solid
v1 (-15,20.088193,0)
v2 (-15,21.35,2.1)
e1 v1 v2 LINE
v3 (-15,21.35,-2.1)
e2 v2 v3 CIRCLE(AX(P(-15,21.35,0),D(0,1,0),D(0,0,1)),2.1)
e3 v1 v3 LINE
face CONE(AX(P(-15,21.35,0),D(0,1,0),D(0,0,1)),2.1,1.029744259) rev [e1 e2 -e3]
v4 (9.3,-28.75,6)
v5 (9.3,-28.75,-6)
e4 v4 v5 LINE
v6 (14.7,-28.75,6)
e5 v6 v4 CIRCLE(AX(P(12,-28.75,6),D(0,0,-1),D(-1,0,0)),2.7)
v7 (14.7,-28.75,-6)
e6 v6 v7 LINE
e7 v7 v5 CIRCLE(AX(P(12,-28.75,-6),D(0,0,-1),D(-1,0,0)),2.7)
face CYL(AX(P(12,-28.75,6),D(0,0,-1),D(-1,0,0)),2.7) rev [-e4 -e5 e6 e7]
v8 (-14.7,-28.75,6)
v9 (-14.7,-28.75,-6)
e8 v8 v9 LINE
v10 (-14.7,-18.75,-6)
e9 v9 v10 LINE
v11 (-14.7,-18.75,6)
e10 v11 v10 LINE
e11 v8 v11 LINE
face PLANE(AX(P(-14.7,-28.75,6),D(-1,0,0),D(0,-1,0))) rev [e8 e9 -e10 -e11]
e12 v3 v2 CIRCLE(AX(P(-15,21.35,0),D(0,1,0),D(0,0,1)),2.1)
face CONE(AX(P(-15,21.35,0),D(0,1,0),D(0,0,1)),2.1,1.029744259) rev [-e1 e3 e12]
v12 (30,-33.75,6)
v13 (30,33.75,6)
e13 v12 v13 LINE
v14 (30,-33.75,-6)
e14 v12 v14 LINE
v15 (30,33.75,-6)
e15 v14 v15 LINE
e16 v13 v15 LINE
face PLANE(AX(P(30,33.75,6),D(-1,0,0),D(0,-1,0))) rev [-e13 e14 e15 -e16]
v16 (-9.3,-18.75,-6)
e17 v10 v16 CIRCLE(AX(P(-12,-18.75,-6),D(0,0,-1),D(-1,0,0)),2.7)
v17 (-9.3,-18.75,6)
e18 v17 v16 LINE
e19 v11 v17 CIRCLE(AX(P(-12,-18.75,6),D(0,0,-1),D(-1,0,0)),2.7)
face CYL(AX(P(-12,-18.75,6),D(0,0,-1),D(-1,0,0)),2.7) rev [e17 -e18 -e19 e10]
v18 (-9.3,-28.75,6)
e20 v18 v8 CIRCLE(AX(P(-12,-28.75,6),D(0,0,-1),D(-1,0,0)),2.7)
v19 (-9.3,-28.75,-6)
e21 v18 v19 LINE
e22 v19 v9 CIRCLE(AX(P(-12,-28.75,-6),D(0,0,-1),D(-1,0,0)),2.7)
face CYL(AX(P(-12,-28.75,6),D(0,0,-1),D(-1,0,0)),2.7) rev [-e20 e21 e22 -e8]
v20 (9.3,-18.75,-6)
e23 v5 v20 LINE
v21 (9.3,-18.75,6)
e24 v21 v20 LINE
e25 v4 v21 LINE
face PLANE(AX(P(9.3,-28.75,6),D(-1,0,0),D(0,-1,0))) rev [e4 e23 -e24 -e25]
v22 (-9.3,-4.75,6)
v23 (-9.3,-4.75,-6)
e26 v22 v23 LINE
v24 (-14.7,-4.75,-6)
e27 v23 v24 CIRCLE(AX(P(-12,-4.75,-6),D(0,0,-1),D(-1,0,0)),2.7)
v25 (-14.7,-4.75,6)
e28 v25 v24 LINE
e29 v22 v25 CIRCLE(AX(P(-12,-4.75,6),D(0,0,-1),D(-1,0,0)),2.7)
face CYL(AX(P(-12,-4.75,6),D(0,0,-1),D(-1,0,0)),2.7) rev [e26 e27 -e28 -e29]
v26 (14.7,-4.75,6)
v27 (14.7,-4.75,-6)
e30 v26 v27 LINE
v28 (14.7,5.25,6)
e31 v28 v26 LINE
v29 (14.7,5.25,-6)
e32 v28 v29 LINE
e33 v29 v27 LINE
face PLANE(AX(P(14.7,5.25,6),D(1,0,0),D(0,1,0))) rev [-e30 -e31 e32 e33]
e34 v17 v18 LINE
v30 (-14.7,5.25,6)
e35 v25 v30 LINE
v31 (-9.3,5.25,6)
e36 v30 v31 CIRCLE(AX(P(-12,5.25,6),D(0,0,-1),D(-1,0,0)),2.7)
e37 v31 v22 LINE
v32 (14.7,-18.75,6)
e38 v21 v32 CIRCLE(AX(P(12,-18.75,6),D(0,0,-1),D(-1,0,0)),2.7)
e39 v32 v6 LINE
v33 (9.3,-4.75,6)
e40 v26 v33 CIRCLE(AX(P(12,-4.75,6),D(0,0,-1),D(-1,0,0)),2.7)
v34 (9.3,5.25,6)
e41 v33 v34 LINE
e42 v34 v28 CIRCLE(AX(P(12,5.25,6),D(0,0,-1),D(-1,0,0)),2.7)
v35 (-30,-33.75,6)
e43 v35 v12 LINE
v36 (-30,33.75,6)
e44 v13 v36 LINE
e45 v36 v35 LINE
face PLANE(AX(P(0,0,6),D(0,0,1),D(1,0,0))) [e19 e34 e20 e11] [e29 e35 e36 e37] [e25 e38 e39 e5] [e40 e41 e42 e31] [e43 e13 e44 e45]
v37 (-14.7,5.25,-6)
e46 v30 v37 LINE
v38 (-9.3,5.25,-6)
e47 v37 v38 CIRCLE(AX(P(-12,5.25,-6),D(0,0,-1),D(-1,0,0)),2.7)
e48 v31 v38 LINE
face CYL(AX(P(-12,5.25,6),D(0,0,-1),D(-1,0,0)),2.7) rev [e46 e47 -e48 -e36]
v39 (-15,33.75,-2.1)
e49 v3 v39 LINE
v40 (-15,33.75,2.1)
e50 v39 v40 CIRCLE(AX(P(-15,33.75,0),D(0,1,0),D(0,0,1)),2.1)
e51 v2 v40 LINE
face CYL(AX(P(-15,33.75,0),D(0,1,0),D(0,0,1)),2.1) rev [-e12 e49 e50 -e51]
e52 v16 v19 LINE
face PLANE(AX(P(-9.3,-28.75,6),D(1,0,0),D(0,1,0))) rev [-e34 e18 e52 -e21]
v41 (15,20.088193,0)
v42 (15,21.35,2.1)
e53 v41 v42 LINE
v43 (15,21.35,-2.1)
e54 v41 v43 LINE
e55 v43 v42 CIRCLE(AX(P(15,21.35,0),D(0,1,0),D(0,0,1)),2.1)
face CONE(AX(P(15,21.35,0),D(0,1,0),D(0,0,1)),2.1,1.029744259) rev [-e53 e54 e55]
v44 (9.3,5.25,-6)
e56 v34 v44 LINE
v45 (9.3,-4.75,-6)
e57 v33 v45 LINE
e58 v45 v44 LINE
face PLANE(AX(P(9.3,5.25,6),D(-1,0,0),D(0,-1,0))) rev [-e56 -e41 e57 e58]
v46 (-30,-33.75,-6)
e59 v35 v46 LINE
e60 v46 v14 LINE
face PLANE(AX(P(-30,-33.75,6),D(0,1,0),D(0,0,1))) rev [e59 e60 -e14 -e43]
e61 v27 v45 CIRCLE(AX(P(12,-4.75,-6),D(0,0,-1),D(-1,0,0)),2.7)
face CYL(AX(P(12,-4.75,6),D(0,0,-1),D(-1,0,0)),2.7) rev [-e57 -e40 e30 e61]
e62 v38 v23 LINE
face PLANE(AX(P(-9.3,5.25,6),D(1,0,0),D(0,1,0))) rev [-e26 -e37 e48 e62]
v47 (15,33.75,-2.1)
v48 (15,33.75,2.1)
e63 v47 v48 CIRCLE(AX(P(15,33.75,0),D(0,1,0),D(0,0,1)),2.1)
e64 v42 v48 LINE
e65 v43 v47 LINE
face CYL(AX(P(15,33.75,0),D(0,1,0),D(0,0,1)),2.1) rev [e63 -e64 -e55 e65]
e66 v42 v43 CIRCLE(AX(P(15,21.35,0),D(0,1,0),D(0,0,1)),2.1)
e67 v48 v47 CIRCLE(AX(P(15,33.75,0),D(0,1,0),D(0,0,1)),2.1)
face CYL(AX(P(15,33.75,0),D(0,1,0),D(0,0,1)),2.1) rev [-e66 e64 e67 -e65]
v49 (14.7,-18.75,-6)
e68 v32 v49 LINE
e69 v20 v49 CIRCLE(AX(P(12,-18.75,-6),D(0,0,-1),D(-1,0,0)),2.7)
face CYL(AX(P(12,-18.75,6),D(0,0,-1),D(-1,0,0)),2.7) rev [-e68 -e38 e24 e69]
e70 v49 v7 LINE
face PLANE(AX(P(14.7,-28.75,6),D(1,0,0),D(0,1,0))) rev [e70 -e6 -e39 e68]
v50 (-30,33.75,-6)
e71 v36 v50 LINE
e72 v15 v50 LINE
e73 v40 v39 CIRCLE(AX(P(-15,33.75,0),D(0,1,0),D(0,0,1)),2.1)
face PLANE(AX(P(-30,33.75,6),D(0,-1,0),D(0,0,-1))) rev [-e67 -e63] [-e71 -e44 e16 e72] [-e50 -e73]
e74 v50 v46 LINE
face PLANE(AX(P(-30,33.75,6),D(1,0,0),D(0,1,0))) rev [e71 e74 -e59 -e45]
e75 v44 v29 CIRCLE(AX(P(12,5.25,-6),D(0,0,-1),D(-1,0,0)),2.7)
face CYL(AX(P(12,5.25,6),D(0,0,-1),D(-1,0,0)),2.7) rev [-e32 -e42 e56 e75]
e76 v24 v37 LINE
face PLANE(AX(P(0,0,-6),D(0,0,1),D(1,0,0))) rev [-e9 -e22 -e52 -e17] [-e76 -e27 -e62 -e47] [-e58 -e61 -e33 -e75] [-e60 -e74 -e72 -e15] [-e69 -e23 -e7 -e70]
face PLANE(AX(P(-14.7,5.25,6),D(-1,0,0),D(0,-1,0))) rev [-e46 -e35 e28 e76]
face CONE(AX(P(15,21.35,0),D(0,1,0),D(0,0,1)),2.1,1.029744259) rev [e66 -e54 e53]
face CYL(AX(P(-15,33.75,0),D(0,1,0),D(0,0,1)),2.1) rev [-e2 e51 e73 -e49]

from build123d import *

# Parameters (mm, degrees)
SKETCH_1_W             = 60
SKETCH_1_H             = 67.5
EXTRUDE_1_DEPTH        = 6
CUT_EXTRUDE_1_DEPTH    = 47.723254382
HOLE_WIZARD_M5_1_D     = 4.2
HOLE_WIZARD_M5_1_DEPTH = 12.4
HOLE_WIZARD_M5_1_TIP   = 1.2618073


with BuildPart() as part:
    # 草图1 → 凸台-拉伸1 (new, symmetric)
    with BuildSketch(Plane.XY):
        Rectangle(SKETCH_1_W, SKETCH_1_H)
    extrude(amount=EXTRUDE_1_DEPTH, both=True)

    # 草图2 → 切除-拉伸1 (cut, through all)
    with BuildSketch(Plane(origin=(0, 0, -6), x_dir=(-1, 0, 0), z_dir=(0, 0, -1))):
        with BuildLine():
            Line((9.3, -28.75), (9.3, -18.75))
            ThreePointArc((9.3, -18.75), (12, -16.05), (14.7, -18.75))
            Line((14.7, -18.75), (14.7, -28.75))
            ThreePointArc((14.7, -28.75), (12, -31.45), (9.3, -28.75))
        make_face()
        with BuildLine():
            Line((-14.7, -28.75), (-14.7, -18.75))
            ThreePointArc((-14.7, -18.75), (-12, -16.05), (-9.3, -18.75))
            Line((-9.3, -18.75), (-9.3, -28.75))
            ThreePointArc((-9.3, -28.75), (-12, -31.45), (-14.7, -28.75))
        make_face()
        with BuildLine():
            Line((14.7, 5.25), (14.7, -4.75))
            ThreePointArc((14.7, -4.75), (12, -7.45), (9.3, -4.75))
            Line((9.3, -4.75), (9.3, 5.25))
            ThreePointArc((9.3, 5.25), (12, 7.95), (14.7, 5.25))
        make_face()
        with BuildLine():
            Line((-9.3, 5.25), (-9.3, -4.75))
            ThreePointArc((-9.3, -4.75), (-12, -7.45), (-14.7, -4.75))
            Line((-14.7, -4.75), (-14.7, 5.25))
            ThreePointArc((-14.7, 5.25), (-12, 7.95), (-9.3, 5.25))
        make_face()
    extrude(amount=-CUT_EXTRUDE_1_DEPTH, mode=Mode.SUBTRACT)

    # M5 螺纹孔1
    with Locations(Plane(origin=(0, 33.75, 0), x_dir=(1, 0, 0), z_dir=(0, 1, 0))):
        with Locations((-15, 0), (15, 0)):
            Hole(HOLE_WIZARD_M5_1_D / 2, depth=HOLE_WIZARD_M5_1_DEPTH)
            with Locations((0, 0, -(HOLE_WIZARD_M5_1_DEPTH + HOLE_WIZARD_M5_1_TIP / 2))):  # 118° drill point
                Cone(0, HOLE_WIZARD_M5_1_D / 2, HOLE_WIZARD_M5_1_TIP, mode=Mode.SUBTRACT)


solid = part.part
